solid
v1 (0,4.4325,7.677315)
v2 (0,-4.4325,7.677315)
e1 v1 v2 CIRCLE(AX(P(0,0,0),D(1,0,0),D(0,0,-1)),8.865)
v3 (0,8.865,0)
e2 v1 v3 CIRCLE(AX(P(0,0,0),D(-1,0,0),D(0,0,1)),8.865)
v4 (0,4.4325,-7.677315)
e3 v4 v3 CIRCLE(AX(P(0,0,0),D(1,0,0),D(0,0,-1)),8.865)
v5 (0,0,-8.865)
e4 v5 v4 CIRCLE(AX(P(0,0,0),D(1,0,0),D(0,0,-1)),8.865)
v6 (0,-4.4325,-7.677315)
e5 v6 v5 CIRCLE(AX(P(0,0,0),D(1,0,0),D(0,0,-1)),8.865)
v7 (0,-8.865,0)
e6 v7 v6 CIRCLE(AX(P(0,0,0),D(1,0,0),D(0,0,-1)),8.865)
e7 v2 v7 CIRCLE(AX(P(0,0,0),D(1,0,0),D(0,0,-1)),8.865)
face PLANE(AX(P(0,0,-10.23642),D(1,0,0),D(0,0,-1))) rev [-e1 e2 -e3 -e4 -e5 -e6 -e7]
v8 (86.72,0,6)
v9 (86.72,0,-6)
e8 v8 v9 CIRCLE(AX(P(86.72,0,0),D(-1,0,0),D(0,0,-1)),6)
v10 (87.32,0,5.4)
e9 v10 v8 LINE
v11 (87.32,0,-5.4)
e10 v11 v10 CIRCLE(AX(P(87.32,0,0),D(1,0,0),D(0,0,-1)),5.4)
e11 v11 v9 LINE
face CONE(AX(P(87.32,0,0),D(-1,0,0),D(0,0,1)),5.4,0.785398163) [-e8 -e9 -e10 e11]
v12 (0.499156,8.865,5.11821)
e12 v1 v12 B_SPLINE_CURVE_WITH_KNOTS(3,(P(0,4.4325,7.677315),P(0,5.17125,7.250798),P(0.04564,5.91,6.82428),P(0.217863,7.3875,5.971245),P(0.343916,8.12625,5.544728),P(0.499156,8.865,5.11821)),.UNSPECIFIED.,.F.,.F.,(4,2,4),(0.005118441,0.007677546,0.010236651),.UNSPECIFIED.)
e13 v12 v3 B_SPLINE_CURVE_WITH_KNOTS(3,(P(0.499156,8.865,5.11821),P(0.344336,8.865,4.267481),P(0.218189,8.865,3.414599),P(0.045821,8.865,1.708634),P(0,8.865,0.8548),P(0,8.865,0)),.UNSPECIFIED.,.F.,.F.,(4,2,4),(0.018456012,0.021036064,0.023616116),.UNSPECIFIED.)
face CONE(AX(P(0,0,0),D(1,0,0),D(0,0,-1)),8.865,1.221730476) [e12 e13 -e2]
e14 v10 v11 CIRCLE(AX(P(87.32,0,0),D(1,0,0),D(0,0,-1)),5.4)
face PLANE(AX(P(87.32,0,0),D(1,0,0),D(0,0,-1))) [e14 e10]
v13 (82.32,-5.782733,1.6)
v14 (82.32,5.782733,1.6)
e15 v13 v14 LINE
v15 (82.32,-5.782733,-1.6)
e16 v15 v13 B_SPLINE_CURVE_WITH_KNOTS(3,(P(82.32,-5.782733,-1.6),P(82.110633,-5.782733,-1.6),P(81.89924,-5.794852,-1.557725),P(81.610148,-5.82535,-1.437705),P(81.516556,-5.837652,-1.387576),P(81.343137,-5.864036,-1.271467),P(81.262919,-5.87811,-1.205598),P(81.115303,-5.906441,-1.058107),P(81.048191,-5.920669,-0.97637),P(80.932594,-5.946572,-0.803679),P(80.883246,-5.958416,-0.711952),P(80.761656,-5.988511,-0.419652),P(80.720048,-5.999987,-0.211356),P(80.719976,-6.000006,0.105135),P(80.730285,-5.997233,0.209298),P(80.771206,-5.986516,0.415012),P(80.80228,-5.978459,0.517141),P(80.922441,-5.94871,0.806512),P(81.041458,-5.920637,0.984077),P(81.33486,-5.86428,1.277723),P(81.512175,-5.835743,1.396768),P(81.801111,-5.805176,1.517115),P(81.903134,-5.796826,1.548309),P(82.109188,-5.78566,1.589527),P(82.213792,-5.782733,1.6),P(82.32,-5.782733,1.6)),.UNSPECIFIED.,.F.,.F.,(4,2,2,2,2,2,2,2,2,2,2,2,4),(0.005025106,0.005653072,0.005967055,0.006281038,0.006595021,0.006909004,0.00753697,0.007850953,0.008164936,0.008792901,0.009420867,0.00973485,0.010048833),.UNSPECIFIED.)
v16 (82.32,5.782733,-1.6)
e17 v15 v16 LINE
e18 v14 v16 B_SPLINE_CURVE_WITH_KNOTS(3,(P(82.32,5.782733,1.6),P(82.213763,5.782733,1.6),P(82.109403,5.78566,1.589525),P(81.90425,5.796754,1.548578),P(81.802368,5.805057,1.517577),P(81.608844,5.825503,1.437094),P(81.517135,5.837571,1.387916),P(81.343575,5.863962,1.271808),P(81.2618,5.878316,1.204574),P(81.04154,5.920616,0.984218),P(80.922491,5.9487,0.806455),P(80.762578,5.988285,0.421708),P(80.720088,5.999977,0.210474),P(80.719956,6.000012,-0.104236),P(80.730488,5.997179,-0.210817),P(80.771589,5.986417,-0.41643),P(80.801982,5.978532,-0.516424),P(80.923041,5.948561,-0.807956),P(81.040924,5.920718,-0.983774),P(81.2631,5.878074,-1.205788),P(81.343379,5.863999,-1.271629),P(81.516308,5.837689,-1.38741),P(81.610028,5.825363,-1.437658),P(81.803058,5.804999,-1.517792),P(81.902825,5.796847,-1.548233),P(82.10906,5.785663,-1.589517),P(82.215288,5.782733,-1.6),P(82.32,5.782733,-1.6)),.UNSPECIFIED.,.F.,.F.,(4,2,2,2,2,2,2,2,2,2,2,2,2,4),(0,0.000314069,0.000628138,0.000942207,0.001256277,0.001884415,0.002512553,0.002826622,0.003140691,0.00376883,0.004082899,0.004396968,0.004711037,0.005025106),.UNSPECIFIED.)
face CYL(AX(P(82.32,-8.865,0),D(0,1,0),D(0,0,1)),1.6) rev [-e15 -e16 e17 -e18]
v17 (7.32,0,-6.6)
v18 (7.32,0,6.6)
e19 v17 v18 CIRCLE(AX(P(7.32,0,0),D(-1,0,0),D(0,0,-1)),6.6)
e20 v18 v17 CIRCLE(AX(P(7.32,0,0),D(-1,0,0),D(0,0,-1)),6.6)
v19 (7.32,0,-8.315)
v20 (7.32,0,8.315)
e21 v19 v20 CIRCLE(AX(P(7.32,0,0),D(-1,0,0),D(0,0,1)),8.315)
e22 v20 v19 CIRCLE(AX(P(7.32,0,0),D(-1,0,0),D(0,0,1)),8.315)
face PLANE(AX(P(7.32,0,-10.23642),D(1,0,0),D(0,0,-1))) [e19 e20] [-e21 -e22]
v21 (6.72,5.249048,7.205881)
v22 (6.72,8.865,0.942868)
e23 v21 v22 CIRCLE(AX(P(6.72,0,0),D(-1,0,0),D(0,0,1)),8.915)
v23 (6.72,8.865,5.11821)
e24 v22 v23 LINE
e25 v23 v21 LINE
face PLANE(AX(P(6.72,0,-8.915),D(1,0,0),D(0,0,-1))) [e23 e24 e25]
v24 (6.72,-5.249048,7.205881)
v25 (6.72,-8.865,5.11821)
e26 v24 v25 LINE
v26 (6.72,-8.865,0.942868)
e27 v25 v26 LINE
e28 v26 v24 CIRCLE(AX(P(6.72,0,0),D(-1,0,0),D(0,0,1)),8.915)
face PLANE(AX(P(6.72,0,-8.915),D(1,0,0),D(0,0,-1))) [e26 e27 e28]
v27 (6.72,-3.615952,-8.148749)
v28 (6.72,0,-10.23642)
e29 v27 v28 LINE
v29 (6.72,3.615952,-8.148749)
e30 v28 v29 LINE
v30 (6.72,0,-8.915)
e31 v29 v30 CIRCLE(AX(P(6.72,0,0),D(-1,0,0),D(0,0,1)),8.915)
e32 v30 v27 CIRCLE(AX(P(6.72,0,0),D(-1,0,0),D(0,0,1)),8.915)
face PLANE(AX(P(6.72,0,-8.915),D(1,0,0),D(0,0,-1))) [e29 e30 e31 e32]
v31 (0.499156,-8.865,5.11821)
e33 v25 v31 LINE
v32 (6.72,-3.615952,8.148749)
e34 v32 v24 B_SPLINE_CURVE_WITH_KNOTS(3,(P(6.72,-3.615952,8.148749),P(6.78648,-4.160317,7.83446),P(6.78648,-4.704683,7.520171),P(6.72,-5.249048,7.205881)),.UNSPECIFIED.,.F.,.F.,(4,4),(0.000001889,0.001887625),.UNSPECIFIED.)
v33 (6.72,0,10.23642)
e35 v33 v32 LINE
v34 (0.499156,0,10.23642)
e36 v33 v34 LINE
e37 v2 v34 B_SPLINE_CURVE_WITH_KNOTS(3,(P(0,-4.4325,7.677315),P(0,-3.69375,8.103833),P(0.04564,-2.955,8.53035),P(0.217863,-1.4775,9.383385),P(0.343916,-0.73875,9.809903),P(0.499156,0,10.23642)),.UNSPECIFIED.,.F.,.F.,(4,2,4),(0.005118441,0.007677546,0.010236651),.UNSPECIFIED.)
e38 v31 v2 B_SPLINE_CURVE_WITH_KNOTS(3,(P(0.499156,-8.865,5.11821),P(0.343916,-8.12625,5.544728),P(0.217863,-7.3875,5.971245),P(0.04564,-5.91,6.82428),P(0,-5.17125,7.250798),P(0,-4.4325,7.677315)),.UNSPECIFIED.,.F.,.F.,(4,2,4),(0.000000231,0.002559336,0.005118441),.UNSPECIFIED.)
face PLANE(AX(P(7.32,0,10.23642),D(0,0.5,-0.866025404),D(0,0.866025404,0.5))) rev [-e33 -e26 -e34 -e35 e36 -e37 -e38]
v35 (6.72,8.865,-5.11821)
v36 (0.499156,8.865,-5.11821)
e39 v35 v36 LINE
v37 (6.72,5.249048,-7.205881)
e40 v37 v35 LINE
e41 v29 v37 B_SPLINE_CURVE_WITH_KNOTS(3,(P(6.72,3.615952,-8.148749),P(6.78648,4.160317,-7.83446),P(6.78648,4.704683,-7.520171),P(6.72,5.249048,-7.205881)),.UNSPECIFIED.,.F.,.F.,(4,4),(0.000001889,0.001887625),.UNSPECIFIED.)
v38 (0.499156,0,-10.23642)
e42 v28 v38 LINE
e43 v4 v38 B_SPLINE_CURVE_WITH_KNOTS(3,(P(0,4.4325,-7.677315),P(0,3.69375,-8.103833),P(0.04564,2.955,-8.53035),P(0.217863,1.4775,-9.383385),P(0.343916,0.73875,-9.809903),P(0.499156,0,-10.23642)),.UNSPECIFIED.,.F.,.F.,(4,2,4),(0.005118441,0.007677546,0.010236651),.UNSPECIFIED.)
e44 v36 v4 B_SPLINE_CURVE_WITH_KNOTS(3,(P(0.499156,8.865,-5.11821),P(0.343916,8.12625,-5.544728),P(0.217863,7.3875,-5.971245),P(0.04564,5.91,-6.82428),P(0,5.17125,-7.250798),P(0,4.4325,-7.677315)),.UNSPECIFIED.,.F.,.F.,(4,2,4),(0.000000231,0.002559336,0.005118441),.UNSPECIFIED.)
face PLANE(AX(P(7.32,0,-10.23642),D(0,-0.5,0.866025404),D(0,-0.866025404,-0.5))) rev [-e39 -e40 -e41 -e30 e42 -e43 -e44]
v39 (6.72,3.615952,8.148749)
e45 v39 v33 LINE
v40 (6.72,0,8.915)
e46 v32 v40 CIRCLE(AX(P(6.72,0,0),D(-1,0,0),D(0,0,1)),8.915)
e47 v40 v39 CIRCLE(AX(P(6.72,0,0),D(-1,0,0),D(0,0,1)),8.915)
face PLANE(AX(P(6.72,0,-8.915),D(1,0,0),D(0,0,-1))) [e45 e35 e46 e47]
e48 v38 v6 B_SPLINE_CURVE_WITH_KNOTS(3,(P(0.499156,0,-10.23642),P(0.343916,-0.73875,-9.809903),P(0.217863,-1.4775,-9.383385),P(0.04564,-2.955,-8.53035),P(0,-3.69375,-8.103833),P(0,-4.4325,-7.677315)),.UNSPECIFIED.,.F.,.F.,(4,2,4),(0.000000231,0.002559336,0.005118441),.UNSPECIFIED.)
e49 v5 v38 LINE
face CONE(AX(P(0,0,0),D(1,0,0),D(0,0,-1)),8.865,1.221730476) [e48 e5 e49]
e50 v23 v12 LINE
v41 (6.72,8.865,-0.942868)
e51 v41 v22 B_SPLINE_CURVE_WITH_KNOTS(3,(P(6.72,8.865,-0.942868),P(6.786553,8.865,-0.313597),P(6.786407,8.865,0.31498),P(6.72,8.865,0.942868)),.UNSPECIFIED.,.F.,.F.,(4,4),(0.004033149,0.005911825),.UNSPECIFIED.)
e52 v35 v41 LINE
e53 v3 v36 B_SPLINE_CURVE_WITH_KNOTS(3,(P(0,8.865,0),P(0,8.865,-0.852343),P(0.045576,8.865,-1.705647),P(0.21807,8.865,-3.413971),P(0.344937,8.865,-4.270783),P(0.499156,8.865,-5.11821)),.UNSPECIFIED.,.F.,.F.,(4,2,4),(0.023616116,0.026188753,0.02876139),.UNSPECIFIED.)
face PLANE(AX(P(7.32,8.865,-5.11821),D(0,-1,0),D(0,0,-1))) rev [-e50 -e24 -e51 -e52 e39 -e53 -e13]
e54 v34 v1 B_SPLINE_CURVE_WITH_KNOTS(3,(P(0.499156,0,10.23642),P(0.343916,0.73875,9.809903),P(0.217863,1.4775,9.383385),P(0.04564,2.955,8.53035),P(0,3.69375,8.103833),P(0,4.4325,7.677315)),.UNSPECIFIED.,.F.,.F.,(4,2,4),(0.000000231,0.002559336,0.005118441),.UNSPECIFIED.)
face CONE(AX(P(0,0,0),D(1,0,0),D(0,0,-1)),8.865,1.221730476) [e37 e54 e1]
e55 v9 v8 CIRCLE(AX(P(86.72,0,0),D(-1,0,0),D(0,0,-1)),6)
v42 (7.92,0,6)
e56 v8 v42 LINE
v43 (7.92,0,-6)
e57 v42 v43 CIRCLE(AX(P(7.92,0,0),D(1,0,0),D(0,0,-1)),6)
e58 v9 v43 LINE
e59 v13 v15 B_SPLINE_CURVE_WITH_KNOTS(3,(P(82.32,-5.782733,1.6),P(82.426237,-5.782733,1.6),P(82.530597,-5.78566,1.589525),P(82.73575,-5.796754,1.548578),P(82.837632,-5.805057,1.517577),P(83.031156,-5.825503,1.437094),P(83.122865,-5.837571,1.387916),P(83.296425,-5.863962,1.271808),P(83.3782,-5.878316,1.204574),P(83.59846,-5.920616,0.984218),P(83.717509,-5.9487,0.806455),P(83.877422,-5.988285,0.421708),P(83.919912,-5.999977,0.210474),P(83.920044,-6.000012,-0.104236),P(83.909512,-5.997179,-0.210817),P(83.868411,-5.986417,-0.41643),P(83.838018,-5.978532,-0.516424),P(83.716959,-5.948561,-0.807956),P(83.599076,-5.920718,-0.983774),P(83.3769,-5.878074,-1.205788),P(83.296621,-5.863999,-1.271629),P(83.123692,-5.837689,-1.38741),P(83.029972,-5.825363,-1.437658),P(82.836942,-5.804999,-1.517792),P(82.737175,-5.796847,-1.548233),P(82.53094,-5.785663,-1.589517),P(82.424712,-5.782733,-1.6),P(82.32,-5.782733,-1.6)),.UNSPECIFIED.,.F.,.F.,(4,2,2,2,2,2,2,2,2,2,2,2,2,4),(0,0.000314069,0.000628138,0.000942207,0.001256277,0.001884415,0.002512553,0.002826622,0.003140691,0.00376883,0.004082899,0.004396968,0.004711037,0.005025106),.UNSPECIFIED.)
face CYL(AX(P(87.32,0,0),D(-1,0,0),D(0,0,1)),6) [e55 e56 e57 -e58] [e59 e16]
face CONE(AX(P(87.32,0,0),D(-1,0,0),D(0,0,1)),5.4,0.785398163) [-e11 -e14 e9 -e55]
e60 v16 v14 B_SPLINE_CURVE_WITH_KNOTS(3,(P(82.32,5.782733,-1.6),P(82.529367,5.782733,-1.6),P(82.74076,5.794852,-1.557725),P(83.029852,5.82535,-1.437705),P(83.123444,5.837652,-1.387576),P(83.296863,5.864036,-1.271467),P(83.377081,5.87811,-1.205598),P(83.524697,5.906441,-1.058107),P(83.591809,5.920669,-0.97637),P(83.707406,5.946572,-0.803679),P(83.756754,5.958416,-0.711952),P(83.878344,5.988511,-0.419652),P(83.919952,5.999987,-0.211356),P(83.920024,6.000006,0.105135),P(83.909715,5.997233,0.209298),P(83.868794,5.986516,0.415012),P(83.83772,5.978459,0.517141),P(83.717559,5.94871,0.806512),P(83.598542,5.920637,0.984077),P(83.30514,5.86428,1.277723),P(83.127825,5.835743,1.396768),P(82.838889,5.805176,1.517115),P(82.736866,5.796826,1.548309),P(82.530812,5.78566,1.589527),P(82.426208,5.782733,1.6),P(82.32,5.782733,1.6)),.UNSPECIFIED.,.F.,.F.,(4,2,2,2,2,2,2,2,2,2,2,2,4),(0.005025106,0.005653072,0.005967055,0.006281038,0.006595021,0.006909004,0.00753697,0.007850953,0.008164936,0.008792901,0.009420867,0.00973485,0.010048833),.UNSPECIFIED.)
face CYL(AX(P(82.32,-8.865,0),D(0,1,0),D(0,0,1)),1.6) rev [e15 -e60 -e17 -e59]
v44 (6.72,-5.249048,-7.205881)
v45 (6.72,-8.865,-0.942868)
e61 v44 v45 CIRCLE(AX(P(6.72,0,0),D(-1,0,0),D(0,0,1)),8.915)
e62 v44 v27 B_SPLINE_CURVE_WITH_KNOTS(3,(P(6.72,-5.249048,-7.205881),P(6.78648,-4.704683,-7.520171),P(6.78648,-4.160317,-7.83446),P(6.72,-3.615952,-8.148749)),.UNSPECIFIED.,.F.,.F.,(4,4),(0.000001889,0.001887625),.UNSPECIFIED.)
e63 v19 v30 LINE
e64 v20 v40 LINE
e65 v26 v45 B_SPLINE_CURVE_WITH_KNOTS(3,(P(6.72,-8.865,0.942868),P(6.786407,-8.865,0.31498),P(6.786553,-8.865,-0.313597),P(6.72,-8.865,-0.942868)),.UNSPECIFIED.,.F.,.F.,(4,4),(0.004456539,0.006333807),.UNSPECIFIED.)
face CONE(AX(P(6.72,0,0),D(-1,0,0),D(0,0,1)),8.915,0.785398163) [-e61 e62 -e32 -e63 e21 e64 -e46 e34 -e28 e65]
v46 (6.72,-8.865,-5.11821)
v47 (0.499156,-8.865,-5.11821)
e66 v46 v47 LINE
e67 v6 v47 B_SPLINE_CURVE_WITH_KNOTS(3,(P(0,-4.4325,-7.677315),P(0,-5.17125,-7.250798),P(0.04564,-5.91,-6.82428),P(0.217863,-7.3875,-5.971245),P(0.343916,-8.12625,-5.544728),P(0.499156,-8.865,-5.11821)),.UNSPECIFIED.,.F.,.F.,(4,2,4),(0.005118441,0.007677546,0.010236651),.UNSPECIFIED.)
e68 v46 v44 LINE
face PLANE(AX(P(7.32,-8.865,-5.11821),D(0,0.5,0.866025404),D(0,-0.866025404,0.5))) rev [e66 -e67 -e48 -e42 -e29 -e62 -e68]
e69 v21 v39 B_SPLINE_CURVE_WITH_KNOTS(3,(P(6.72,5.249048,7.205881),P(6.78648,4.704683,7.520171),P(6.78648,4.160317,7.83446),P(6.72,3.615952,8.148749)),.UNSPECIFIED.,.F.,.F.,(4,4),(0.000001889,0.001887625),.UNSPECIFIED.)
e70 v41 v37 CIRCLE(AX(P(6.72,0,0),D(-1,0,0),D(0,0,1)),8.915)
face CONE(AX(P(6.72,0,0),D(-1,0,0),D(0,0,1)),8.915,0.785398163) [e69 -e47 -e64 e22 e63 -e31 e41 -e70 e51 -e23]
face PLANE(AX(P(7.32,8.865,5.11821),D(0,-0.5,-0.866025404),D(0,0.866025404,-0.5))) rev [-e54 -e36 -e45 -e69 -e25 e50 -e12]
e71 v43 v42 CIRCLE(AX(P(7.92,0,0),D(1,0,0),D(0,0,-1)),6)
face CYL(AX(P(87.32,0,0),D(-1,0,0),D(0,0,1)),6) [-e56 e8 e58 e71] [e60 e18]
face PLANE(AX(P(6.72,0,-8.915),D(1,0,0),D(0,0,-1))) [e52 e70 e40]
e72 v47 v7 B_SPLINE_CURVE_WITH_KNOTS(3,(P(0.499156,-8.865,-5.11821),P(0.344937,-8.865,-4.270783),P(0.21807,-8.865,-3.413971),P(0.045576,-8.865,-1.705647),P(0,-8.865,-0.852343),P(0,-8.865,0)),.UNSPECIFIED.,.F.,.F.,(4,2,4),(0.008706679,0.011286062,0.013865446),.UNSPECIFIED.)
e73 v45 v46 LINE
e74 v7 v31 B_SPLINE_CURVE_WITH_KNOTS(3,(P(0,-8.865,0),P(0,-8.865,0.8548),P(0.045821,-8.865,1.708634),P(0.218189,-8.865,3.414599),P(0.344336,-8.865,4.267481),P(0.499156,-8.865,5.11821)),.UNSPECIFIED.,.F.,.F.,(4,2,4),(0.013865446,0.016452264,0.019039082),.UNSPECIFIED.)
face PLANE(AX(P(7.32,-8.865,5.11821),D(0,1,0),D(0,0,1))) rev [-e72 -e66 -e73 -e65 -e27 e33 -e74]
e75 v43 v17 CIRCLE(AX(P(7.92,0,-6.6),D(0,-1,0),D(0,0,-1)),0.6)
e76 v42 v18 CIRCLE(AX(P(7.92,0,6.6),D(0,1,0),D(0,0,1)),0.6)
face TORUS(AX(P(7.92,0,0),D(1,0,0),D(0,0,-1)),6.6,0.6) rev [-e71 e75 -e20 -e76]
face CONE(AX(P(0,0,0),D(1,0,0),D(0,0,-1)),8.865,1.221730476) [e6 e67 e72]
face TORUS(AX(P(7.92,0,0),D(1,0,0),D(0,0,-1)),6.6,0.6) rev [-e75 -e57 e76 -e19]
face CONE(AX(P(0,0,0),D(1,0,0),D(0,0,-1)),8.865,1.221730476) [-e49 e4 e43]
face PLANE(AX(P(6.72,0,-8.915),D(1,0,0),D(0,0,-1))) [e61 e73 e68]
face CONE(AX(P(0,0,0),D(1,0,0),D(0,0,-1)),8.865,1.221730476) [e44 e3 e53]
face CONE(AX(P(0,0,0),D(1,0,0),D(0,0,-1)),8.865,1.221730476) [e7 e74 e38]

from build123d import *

# Parameters (mm, degrees)
BASEHEAD_DEPTH  = 7.32
SKETCH5_R       = 6
BASEBODY_DEPTH  = 80
CHAMFER1_SIZE   = 0.6
HOLE_DEPTH      = 89.363764774
HOLE_DEPTH_BACK = 89.363764774
SKETCH6_R       = 1.6
HEADFILLET_R    = 0.6


with BuildPart() as part:
    # Sketch2 → BaseHead (new body)
    with BuildSketch(Plane(origin=(0, 0, 0), x_dir=(0, 0, -1), z_dir=(1, 0, 0))):
        Polygon((10.236420273, 0), (5.118210136, 8.865), (-5.118210136, 8.865), (-10.236420273, 0), (-5.118210136, -8.865), (5.118210136, -8.865), align=None)
    extrude(amount=BASEHEAD_DEPTH)

    # Sketch3 → BearingFace (revolve, cut)
    with BuildSketch(Plane(origin=(0, 0, 0), x_dir=(1, 0, 0), z_dir=(0, 1, 0)), mode=Mode.PRIVATE) as bearingface_sk:
        Polygon((7.32, 10.236420273), (7.32, 8.315), (6.72, 8.915), (6.72, 10.236420273), align=None)
    revolve(bearingface_sk.sketch.rotate(Axis((-0.957090588, 0, 0), (1, 0, 0)), 180), axis=Axis((-0.957090588, 0, 0), (1, 0, 0)), mode=Mode.SUBTRACT)

    # Sketch4 → HeadChamfer (revolve, cut)
    with BuildSketch(Plane(origin=(0, 0, 0), x_dir=(1, 0, 0), z_dir=(0, 1, 0))):
        Polygon((0, 10.236420273), (0.499156158, 10.236420273), (0, 8.865), align=None)
    revolve(axis=Axis((-0.493528746, 0, 0), (1, 0, 0)), mode=Mode.SUBTRACT)

    # Sketch5 → BaseBody (add)
    with BuildSketch(Plane(origin=(7.32, 0, 0), x_dir=(0, 0, -1), z_dir=(1, 0, 0))):
        Circle(SKETCH5_R)
    extrude(amount=BASEBODY_DEPTH)

    # Chamfer1
    chamfer1_edges = [part.edges().sort_by_distance(p)[0] for p in [
        (87.32, 0, 6),
    ]]
    chamfer(chamfer1_edges, length=CHAMFER1_SIZE)

    # Sketch6 → Hole (cut, two sides: drawn at the far end of the back side and taken through both)
    with BuildSketch(Plane(origin=(0, 0, 0), x_dir=(1, 0, 0), z_dir=(0, 1, 0)).offset(-HOLE_DEPTH_BACK)):
        with Locations(Location((82.32, 0, 0), (0, 0, 270))):
            Circle(SKETCH6_R)
    extrude(amount=HOLE_DEPTH + HOLE_DEPTH_BACK, mode=Mode.SUBTRACT)

    # HeadFillet
    headfillet_edges = [part.edges().sort_by_distance(p)[0] for p in [
        (7.32, 0, 6),
    ]]
    fillet(headfillet_edges, radius=HEADFILLET_R)


solid = part.part
